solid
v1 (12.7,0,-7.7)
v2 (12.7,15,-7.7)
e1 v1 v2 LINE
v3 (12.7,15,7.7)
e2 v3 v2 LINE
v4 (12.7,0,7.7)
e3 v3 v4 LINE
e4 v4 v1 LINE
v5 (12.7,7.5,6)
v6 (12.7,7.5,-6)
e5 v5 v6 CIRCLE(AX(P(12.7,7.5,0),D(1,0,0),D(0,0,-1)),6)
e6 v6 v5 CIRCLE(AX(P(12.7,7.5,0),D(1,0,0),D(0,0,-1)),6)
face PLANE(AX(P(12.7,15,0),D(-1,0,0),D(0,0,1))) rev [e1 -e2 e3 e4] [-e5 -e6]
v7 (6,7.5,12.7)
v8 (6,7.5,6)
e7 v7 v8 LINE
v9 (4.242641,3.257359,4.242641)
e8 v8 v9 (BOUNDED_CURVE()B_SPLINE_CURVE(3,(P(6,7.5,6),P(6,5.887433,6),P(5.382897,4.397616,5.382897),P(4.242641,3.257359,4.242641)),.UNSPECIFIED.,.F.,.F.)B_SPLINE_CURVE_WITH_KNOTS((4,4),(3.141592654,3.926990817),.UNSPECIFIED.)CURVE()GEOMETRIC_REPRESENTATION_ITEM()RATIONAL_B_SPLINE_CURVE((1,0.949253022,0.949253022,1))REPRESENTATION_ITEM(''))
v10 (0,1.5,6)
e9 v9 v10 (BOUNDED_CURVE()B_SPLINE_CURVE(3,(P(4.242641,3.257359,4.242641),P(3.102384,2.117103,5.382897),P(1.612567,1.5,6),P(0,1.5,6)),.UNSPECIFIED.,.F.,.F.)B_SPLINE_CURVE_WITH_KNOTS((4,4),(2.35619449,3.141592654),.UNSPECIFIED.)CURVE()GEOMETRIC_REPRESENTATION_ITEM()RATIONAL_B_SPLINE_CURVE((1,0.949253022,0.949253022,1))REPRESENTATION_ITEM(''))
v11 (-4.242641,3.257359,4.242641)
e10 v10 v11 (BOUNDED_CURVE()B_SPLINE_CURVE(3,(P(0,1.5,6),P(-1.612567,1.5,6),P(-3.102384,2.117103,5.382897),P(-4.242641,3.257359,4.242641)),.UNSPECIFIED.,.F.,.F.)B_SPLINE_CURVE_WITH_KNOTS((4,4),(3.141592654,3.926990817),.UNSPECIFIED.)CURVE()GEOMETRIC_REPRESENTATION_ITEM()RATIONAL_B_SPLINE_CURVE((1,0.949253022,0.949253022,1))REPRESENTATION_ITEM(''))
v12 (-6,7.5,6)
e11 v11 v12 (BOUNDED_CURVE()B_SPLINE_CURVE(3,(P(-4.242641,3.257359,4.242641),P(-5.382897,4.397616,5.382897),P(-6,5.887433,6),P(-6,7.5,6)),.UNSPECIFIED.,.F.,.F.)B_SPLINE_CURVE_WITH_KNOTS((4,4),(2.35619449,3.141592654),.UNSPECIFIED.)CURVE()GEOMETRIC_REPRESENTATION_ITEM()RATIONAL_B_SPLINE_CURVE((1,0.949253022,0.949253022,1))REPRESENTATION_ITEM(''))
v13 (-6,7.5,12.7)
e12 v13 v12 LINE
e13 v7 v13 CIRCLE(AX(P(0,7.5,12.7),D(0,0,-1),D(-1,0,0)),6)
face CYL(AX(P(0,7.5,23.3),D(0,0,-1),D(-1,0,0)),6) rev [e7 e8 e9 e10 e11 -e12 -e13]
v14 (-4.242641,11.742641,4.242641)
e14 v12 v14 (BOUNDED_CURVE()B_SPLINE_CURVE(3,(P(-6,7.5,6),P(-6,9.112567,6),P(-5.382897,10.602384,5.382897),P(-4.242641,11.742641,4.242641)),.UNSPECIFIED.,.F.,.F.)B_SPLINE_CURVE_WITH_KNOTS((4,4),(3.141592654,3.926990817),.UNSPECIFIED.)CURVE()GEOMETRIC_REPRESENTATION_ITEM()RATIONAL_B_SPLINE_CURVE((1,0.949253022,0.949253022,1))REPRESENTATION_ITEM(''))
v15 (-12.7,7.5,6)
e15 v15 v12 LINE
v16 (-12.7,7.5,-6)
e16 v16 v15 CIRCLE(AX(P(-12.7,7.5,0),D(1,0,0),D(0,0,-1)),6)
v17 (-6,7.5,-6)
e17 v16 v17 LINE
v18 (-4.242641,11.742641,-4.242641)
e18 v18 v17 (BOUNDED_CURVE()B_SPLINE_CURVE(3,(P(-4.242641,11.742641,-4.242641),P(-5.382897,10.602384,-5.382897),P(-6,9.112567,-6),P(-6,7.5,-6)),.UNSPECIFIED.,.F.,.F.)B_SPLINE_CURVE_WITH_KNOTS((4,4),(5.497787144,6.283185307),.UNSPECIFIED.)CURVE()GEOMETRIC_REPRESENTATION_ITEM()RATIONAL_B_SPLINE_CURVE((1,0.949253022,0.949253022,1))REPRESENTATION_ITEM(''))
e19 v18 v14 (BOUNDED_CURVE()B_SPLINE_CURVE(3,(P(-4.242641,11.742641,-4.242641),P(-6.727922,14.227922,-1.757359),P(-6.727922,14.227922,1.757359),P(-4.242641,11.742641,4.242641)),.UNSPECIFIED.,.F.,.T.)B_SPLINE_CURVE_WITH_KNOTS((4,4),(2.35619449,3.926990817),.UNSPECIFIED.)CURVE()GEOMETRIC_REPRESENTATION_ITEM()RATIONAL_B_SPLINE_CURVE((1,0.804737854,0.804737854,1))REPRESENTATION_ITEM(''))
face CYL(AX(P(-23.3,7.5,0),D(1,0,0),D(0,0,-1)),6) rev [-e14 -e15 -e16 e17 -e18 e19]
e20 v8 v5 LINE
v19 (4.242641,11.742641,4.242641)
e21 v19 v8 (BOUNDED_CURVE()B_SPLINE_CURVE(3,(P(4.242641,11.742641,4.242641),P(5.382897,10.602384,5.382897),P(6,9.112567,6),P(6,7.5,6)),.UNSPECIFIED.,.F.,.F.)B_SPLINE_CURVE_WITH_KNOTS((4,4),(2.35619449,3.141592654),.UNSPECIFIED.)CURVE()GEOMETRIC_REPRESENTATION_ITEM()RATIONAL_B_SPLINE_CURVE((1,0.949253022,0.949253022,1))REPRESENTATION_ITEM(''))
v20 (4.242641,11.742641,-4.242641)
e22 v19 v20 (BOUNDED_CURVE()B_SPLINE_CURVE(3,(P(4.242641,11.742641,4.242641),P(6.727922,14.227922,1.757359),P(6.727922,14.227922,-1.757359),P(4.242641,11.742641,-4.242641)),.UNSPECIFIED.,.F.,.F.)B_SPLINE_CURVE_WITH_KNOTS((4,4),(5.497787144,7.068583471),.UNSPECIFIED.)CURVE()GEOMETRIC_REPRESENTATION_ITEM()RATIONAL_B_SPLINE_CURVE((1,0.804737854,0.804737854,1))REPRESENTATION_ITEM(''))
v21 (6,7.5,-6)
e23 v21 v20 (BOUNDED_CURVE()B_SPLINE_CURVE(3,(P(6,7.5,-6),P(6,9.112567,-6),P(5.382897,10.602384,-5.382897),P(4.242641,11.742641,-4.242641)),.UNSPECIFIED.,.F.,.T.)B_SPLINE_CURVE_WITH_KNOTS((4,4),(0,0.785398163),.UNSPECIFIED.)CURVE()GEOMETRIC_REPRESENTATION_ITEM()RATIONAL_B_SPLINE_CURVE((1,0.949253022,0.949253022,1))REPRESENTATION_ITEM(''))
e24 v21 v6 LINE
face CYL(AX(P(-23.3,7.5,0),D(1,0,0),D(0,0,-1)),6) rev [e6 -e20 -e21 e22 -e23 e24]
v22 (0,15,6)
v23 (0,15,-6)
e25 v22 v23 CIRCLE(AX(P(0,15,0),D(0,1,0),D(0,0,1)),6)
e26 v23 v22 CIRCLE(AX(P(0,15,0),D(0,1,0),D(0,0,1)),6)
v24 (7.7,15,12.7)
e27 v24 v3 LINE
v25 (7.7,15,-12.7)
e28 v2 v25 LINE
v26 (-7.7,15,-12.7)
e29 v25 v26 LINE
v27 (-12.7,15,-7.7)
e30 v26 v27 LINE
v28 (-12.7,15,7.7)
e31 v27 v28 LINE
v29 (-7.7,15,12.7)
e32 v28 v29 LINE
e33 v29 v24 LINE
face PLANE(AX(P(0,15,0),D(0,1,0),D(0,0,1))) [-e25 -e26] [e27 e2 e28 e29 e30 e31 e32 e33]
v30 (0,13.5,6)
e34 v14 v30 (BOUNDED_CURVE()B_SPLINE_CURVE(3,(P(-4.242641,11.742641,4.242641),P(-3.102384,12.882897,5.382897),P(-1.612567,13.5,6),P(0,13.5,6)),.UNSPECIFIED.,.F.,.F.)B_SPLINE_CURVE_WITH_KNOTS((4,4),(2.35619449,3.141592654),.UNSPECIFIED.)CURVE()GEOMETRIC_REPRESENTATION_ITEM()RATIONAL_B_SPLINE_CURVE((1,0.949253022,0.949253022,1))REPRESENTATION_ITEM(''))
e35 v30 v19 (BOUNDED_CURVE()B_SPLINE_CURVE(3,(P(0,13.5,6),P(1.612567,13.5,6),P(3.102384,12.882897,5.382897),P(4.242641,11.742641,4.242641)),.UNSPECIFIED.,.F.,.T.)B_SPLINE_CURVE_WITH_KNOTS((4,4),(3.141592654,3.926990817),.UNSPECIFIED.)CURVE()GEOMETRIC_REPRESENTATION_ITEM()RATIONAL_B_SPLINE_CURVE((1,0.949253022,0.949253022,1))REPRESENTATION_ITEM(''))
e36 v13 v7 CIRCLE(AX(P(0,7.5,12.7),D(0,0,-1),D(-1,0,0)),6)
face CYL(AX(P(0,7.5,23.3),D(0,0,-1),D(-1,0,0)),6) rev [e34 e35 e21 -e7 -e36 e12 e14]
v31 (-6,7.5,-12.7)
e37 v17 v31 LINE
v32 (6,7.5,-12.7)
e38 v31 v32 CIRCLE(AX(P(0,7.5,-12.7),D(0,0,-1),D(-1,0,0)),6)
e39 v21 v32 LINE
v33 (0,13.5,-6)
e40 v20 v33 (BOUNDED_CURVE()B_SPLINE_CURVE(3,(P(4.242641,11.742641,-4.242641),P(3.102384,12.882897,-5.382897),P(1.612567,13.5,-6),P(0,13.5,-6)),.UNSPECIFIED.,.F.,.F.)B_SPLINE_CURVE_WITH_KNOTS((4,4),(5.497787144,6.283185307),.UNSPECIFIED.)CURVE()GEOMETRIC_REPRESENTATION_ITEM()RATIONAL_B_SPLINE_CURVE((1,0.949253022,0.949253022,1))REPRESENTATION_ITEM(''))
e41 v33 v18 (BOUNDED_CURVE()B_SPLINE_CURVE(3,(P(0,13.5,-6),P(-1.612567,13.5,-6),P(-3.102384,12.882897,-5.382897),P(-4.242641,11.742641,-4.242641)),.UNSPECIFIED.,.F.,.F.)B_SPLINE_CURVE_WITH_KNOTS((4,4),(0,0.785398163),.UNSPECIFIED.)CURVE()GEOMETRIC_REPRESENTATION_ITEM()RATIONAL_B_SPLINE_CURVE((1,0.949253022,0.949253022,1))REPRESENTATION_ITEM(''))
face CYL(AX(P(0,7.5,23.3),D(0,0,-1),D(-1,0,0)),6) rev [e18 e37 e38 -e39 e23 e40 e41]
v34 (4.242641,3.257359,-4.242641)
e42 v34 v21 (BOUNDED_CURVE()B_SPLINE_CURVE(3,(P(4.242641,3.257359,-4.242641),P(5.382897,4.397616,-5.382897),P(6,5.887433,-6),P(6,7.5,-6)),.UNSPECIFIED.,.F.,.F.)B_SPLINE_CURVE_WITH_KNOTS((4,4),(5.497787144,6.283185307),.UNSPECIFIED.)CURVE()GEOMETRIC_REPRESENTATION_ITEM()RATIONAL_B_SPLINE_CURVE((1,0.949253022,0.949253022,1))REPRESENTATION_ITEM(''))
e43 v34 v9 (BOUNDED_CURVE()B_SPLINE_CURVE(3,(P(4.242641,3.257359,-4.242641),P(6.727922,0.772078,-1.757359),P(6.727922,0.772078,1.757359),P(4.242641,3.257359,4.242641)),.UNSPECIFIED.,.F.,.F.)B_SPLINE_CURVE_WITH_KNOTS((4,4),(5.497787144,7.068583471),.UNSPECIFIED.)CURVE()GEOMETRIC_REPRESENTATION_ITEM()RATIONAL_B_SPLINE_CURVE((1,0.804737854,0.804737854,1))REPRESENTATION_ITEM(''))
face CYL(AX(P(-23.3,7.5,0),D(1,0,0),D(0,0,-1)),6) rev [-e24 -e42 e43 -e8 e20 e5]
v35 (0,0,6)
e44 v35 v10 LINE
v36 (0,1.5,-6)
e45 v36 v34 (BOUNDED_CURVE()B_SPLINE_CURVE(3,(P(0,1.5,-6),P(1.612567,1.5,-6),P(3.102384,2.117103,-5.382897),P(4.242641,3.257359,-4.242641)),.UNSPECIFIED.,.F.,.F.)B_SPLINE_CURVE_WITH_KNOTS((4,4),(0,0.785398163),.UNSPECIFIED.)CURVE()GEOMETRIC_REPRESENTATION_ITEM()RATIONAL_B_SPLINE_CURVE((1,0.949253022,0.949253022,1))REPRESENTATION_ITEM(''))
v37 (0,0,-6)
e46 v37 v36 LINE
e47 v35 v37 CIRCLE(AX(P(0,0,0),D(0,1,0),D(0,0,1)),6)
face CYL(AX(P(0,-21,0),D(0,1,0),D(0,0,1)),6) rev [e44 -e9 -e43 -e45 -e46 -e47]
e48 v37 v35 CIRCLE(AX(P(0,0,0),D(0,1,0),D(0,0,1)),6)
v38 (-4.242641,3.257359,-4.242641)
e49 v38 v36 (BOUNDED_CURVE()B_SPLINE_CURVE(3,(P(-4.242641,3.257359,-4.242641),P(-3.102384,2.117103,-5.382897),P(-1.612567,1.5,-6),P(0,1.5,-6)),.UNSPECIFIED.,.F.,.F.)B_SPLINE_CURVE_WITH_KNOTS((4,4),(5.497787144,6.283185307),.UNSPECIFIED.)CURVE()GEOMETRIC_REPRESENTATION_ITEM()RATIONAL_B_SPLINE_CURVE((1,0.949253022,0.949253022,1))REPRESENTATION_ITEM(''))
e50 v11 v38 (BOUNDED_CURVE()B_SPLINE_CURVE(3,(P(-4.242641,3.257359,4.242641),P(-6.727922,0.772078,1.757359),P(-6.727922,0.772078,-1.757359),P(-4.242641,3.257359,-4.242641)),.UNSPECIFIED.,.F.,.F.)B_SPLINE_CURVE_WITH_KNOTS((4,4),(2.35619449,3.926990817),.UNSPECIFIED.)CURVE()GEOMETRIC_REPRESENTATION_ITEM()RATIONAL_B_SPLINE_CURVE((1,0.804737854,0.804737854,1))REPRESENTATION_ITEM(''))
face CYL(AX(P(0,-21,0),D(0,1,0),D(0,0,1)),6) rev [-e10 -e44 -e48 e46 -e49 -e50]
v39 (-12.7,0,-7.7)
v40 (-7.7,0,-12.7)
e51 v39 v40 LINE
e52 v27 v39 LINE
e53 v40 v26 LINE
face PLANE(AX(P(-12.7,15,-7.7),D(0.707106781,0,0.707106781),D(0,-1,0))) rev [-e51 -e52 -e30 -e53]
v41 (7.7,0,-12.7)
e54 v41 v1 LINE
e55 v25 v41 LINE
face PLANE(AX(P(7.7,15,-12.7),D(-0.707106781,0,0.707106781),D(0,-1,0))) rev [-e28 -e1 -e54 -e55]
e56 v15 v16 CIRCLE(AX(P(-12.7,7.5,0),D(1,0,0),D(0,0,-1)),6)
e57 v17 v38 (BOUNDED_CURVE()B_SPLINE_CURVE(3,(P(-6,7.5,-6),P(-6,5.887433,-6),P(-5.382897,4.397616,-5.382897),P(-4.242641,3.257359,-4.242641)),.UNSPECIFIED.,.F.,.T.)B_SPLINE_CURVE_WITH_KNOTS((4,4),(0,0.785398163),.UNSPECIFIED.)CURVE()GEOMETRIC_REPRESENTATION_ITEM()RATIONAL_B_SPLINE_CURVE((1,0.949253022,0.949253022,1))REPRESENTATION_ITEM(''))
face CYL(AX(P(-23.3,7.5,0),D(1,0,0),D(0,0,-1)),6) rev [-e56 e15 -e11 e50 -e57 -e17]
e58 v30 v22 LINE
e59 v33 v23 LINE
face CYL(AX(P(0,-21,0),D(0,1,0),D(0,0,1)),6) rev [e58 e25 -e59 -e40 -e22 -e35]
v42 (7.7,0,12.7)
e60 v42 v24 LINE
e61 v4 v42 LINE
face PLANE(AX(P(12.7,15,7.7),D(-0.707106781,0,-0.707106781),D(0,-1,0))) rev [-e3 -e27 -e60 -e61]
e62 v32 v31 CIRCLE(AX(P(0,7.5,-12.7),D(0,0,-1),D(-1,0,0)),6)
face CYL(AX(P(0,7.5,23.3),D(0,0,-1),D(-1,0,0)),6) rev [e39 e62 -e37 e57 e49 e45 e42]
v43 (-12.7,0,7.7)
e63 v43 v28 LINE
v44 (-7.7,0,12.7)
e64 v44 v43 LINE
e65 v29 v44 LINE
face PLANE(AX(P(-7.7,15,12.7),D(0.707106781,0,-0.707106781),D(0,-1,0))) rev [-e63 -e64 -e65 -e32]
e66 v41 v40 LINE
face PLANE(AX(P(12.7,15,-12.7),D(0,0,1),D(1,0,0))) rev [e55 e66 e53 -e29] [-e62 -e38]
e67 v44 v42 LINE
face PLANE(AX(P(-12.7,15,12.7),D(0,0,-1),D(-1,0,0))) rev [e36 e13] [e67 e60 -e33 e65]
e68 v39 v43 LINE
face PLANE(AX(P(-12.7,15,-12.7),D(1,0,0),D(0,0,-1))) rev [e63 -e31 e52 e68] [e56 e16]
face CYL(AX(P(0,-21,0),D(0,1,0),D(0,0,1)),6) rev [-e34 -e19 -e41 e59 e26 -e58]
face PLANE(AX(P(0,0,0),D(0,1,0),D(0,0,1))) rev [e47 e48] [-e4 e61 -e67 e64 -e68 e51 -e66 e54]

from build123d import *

# Parameters (mm, degrees)
BASE_BLOCK_DEPTH       = 15
CORNER_CHAMFER_1_SIZE  = 5
CORNER_CHAMFER_2_SIZE  = 5
CORNER_CHAMFER_3_SIZE  = 5
CORNER_CHAMFER_4_SIZE  = 5
SIDE_HOLE_A_SKETCH_R   = 6
SIDE_HOLE_A_12_DEPTH   = 36
SIDE_HOLE_B_SKETCH_R   = 6
SIDE_HOLE_B_12_DEPTH   = 36
VERTICAL_BORE_SKETCH_R = 6
VERTICAL_BORE_12_DEPTH = 36


with BuildPart() as part:
    # Base Square Sketch → Base Block (new body)
    with BuildSketch(Plane(origin=(0, 0, 0), x_dir=(1, 0, 0), z_dir=(0, 1, 0))):
        Polygon((12.7, 0), (12.7, 12.7), (-12.7, 12.7), (-12.7, -12.7), (12.7, -12.7), align=None)
    extrude(amount=BASE_BLOCK_DEPTH)

    # Corner Chamfer 1
    corner_chamfer_1_edges = [part.edges().sort_by_distance(p)[0] for p in [
        (12.7, 7.5, 12.7),
    ]]
    chamfer(corner_chamfer_1_edges, length=CORNER_CHAMFER_1_SIZE)

    # Corner Chamfer 2
    corner_chamfer_2_edges = [part.edges().sort_by_distance(p)[0] for p in [
        (12.7, 7.5, -12.7),
    ]]
    chamfer(corner_chamfer_2_edges, length=CORNER_CHAMFER_2_SIZE)

    # Corner Chamfer 3
    corner_chamfer_3_edges = [part.edges().sort_by_distance(p)[0] for p in [
        (-12.7, 7.5, -12.7),
    ]]
    chamfer(corner_chamfer_3_edges, length=CORNER_CHAMFER_3_SIZE)

    # Corner Chamfer 4
    corner_chamfer_4_edges = [part.edges().sort_by_distance(p)[0] for p in [
        (-12.7, 7.5, 12.7),
    ]]
    chamfer(corner_chamfer_4_edges, length=CORNER_CHAMFER_4_SIZE)

    # Side Hole A Sketch → Side Hole A Ø12 (cut)
    with BuildSketch(Plane(origin=(0, 0, -12.7), x_dir=(-1, 0, 0), z_dir=(0, 0, -1))):
        with Locations((0, 7.5)):
            Circle(SIDE_HOLE_A_SKETCH_R)
    extrude(amount=-SIDE_HOLE_A_12_DEPTH, mode=Mode.SUBTRACT)

    # Side Hole B Sketch → Side Hole B Ø12 (cut)
    with BuildSketch(Plane(origin=(12.7, 0, 0), x_dir=(0, 0, -1), z_dir=(1, 0, 0))):
        with Locations((0, 7.5)):
            Circle(SIDE_HOLE_B_SKETCH_R)
    extrude(amount=-SIDE_HOLE_B_12_DEPTH, mode=Mode.SUBTRACT)

    # Vertical Bore Sketch → Vertical Bore Ø12 (cut)
    with BuildSketch(Plane(origin=(0, 15, 0), x_dir=(1, 0, 0), z_dir=(0, 1, 0))):
        with Locations(Location((0, 0, 0), (0, 0, 270))):
            Circle(VERTICAL_BORE_SKETCH_R)
    extrude(amount=-VERTICAL_BORE_12_DEPTH, mode=Mode.SUBTRACT)


solid = part.part
